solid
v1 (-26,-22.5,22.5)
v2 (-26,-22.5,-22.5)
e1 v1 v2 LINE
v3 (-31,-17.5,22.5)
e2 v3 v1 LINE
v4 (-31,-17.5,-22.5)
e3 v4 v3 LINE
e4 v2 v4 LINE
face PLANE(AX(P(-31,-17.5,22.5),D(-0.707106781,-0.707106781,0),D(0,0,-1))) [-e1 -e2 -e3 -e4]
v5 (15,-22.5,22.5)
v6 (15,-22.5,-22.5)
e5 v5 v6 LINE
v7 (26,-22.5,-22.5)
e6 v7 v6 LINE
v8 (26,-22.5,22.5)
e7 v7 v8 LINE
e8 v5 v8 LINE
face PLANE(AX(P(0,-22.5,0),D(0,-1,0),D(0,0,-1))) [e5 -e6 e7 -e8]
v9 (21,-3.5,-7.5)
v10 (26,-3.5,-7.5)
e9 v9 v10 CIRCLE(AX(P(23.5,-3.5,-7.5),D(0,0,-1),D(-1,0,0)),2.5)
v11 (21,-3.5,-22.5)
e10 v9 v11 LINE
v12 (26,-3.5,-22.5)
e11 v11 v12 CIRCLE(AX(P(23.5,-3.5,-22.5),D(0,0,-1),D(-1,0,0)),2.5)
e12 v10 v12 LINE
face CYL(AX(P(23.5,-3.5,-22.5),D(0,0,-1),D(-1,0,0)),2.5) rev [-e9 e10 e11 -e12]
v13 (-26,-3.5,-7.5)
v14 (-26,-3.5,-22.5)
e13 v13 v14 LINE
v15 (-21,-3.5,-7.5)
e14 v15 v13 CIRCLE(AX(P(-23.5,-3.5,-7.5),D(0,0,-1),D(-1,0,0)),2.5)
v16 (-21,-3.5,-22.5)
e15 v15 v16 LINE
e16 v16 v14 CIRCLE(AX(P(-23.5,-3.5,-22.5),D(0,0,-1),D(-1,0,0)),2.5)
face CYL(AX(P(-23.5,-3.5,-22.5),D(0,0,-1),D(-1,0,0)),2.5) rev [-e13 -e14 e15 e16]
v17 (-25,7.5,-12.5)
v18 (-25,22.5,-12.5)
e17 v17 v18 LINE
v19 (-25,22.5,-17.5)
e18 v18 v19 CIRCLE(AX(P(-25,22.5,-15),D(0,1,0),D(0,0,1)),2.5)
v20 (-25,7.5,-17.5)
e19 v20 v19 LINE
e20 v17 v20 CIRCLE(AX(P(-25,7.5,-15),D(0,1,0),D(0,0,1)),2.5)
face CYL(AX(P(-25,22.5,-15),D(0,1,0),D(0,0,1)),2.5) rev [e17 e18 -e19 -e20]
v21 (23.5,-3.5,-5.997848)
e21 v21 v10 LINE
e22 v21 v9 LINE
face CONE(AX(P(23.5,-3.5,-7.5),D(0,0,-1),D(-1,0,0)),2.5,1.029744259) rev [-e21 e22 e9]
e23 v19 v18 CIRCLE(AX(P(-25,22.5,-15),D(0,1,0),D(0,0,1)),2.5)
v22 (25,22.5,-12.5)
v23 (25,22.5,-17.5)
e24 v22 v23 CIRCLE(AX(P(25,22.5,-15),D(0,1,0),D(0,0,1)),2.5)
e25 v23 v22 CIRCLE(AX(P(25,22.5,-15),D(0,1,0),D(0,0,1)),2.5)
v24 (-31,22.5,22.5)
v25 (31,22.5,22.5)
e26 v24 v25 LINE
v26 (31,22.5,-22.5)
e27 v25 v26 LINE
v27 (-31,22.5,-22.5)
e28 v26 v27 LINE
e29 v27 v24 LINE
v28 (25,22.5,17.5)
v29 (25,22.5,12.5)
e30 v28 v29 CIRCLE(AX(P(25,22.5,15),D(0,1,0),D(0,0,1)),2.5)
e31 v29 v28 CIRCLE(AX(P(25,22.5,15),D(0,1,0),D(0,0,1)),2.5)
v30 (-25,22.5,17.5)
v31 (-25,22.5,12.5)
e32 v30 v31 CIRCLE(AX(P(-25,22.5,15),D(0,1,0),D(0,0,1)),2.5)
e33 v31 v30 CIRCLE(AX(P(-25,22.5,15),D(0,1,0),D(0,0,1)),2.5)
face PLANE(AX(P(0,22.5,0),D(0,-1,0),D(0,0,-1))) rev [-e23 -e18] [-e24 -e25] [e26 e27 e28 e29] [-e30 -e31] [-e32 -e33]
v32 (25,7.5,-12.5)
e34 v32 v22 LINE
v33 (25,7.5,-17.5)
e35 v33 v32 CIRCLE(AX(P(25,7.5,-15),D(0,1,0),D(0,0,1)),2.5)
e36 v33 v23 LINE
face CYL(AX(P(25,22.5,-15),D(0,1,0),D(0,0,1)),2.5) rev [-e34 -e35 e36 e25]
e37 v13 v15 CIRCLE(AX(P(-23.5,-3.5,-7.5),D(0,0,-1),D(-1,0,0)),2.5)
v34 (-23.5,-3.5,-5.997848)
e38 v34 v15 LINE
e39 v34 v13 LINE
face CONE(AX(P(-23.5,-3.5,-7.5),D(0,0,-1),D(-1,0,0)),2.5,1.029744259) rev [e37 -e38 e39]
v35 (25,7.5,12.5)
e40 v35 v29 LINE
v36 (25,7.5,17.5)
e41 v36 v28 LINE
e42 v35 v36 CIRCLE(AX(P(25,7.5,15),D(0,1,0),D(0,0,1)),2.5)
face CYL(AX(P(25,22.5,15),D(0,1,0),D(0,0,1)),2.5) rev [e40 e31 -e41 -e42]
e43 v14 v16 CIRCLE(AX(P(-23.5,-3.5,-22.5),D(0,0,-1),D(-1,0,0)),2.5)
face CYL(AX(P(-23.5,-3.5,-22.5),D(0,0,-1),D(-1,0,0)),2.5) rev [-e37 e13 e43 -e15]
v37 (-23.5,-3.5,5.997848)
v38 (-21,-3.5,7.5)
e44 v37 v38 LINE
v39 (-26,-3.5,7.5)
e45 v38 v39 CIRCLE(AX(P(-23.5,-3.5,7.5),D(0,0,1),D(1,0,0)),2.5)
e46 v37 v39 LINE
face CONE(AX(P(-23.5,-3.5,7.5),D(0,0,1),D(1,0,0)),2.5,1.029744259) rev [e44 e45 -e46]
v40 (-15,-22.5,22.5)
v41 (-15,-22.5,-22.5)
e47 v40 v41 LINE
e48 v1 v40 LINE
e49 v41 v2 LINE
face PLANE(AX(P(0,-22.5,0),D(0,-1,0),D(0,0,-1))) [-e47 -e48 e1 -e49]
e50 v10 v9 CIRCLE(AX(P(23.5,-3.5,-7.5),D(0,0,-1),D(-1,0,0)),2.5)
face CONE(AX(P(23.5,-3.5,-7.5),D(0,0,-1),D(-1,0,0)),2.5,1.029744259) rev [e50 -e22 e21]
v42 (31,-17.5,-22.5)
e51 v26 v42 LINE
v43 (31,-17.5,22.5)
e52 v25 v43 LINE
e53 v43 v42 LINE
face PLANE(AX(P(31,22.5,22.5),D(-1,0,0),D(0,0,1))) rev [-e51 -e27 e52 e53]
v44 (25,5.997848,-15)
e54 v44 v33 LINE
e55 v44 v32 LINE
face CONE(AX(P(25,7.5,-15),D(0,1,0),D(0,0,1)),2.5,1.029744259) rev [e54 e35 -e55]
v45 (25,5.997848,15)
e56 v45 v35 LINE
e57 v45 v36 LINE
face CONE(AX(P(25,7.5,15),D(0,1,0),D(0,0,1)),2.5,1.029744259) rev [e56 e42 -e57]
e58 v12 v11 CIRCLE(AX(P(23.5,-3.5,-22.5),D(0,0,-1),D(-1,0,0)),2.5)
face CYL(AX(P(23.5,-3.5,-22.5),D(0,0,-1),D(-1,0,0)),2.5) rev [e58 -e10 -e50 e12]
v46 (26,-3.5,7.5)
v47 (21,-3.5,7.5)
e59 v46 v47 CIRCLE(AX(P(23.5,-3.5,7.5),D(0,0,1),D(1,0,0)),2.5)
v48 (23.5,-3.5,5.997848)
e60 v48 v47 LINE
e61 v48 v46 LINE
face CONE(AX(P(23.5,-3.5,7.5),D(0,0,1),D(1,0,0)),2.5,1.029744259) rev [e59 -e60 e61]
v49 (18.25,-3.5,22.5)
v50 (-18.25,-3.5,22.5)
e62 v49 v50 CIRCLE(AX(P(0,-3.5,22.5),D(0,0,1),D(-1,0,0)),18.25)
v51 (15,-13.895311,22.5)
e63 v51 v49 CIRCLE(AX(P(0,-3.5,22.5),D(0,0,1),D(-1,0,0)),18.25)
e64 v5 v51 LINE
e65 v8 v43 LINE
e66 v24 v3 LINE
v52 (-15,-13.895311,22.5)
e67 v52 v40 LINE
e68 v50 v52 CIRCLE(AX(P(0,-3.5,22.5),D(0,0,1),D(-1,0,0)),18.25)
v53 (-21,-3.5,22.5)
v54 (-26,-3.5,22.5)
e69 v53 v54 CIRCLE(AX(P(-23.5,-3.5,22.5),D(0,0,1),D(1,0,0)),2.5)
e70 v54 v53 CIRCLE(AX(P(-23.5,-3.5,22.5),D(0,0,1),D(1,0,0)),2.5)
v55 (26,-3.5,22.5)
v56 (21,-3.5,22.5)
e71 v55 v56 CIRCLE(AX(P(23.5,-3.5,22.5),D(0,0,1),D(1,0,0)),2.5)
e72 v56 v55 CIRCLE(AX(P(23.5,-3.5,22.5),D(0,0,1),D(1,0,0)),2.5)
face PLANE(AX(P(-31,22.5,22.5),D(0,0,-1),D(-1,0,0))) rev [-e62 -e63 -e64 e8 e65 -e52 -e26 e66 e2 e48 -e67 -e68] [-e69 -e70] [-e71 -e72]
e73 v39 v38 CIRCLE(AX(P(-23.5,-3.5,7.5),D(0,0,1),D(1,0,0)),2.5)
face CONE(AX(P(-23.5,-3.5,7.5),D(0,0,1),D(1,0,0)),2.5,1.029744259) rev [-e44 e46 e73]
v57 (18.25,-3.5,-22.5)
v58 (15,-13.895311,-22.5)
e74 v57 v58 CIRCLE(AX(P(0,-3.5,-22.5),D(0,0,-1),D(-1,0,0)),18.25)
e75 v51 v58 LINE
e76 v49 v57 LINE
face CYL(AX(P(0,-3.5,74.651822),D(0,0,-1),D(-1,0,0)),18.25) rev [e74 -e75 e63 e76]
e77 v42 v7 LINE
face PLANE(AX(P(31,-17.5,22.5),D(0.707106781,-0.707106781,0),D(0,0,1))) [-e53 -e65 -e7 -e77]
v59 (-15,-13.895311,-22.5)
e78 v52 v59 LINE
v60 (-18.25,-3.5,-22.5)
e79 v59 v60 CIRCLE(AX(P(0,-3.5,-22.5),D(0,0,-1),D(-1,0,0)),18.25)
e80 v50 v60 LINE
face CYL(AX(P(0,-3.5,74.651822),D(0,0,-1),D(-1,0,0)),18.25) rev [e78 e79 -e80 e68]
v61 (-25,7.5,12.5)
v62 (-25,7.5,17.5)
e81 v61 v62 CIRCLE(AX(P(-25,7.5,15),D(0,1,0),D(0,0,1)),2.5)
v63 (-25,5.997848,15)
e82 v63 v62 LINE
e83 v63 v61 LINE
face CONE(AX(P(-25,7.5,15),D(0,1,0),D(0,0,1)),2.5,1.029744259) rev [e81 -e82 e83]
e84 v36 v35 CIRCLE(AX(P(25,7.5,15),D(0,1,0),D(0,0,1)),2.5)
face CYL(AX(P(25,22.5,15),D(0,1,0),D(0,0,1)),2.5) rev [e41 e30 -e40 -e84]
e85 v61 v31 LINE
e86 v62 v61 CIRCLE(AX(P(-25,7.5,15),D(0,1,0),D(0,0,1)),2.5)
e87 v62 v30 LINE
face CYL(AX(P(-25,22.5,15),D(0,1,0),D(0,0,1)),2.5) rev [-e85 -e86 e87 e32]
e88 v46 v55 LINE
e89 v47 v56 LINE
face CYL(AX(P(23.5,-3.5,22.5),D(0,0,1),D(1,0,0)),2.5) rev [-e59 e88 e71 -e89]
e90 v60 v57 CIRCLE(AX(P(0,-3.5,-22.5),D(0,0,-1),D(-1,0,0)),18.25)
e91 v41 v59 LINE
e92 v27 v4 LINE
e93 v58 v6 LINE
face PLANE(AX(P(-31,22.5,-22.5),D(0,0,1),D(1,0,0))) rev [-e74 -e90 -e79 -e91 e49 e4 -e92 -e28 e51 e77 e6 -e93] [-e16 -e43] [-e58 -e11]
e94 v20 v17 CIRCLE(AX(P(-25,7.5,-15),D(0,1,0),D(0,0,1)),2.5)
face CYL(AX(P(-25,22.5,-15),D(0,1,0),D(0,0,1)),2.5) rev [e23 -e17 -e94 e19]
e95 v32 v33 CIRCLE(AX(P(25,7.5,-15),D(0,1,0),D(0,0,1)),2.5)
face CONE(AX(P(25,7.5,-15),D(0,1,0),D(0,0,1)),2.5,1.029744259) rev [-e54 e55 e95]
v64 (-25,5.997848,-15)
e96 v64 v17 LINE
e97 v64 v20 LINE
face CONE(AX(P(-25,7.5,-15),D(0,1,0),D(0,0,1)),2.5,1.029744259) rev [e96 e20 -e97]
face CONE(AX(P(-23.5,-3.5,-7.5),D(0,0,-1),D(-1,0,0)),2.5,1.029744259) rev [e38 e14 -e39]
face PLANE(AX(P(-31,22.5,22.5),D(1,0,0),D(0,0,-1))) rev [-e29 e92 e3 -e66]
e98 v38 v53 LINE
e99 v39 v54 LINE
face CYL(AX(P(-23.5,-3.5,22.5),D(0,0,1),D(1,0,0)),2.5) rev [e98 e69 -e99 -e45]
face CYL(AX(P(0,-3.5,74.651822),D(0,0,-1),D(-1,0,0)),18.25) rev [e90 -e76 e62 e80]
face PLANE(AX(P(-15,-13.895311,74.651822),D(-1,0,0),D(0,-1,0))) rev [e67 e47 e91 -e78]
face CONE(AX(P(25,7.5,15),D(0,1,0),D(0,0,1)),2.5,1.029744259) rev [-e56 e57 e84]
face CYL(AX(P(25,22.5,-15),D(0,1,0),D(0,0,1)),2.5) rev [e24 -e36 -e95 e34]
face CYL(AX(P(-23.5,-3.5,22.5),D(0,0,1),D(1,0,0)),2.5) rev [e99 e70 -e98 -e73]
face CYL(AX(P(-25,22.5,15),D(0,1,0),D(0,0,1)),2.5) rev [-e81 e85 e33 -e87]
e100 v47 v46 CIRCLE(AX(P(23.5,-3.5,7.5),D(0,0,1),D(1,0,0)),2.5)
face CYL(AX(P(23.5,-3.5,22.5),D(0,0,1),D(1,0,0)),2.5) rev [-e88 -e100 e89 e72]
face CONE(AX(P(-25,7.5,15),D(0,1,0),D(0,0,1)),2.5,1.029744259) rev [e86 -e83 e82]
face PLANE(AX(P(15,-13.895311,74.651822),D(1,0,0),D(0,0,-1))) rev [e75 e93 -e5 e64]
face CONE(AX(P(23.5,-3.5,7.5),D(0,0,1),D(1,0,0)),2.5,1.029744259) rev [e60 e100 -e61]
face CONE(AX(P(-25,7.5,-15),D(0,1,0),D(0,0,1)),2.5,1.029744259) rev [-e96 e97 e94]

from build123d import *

# Parameters (mm, degrees)
SKETCH_1_W                  = 62
SKETCH_1_H                  = 45
EXTRUDE_1_DEPTH             = 22.5
CUT_EXTRUDE_1_DEPTH         = 45
CHAMFER_1_SIZE              = 5
HOLE_WIZARD_M6_1_D          = 5
HOLE_WIZARD_M6_1_DEPTH      = 15
HOLE_WIZARD_M6_1_TIP        = 1.502151548
HOLE_WIZARD_M6_2_AT_2_COUNT = 2
HOLE_WIZARD_M6_2_AT_2_PITCH = 47


with BuildPart() as part:
    # 草图1 → 凸台-拉伸1 (new, symmetric)
    with BuildSketch(Plane(origin=(0, 0, 0), x_dir=(1, 0, 0), z_dir=(0, 1, 0))):
        Rectangle(SKETCH_1_W, SKETCH_1_H)
    extrude(amount=EXTRUDE_1_DEPTH, both=True)

    # 草图2 → 切除-拉伸1 (cut)
    with BuildSketch(Plane(origin=(0, 0, -22.5), x_dir=(-1, 0, 0), z_dir=(0, 0, -1))):
        with BuildLine():
            Line((-15, -13.895311443), (-15, -22.5))
            Line((-15, -22.5), (15, -22.5))
            Line((15, -22.5), (15, -13.895311443))
            ThreePointArc((15, -13.895311443), (0, 14.75), (-15, -13.895311443))
        make_face()
    extrude(amount=-CUT_EXTRUDE_1_DEPTH, mode=Mode.SUBTRACT)

    # 倒角1
    chamfer_1_edges = [part.edges().sort_by_distance(p)[0] for p in [
        (-31, -22.5, 0),
        (31, -22.5, 0),
    ]]
    chamfer(chamfer_1_edges, length=CHAMFER_1_SIZE)

    # M6 螺纹孔1
    with Locations(Plane(origin=(0, 22.5, 0), x_dir=(1, 0, 0), z_dir=(0, 1, 0))):
        with Locations((-25, 15), (-25, -15), (25, -15), (25, 15)):
            Hole(HOLE_WIZARD_M6_1_D / 2, depth=HOLE_WIZARD_M6_1_DEPTH)
            with Locations((0, 0, -(HOLE_WIZARD_M6_1_DEPTH + HOLE_WIZARD_M6_1_TIP / 2))):  # 118° drill point
                Cone(0, HOLE_WIZARD_M6_1_D / 2, HOLE_WIZARD_M6_1_TIP, mode=Mode.SUBTRACT)

    # 草图6 → M6 螺纹孔2 (revolve, cut)
    with BuildSketch(Plane(origin=(23.5, -3.5, -22.5), x_dir=(0, 1, 0), z_dir=(1, 0, 0))):
        Polygon((0, 0), (0, 16.502151548), (2.5, 15), (2.5, 0), align=None)
    hole_wizard_m6_2 = revolve(axis=Axis((23.5, -3.5, -28.85), (0, 0, 1)), mode=Mode.SUBTRACT)

    # M6 螺纹孔2 at 2: M6 螺纹孔2 ×2
    with Locations(*[(-i * HOLE_WIZARD_M6_2_AT_2_PITCH, 0, 0) for i in range(1, HOLE_WIZARD_M6_2_AT_2_COUNT)]):
        add(hole_wizard_m6_2, mode=Mode.SUBTRACT)

    # 镜向1: M6 螺纹孔2 across plane
    add(hole_wizard_m6_2.mirror(Plane.XY), mode=Mode.SUBTRACT)

    # 镜向1 copy 1 sketch → 镜向1 copy 1 (revolve, cut)
    with BuildSketch(Plane(origin=(-23.5, -3.5, 22.5), x_dir=(0, 1, 0), z_dir=(1, 0, 0))):
        Polygon((0, 0), (0, -16.502151548), (2.5, -15), (2.5, 0), align=None)
    revolve(axis=Axis((-23.5, -3.5, 28.85), (0, 0, 1)), mode=Mode.SUBTRACT)


solid = part.part
